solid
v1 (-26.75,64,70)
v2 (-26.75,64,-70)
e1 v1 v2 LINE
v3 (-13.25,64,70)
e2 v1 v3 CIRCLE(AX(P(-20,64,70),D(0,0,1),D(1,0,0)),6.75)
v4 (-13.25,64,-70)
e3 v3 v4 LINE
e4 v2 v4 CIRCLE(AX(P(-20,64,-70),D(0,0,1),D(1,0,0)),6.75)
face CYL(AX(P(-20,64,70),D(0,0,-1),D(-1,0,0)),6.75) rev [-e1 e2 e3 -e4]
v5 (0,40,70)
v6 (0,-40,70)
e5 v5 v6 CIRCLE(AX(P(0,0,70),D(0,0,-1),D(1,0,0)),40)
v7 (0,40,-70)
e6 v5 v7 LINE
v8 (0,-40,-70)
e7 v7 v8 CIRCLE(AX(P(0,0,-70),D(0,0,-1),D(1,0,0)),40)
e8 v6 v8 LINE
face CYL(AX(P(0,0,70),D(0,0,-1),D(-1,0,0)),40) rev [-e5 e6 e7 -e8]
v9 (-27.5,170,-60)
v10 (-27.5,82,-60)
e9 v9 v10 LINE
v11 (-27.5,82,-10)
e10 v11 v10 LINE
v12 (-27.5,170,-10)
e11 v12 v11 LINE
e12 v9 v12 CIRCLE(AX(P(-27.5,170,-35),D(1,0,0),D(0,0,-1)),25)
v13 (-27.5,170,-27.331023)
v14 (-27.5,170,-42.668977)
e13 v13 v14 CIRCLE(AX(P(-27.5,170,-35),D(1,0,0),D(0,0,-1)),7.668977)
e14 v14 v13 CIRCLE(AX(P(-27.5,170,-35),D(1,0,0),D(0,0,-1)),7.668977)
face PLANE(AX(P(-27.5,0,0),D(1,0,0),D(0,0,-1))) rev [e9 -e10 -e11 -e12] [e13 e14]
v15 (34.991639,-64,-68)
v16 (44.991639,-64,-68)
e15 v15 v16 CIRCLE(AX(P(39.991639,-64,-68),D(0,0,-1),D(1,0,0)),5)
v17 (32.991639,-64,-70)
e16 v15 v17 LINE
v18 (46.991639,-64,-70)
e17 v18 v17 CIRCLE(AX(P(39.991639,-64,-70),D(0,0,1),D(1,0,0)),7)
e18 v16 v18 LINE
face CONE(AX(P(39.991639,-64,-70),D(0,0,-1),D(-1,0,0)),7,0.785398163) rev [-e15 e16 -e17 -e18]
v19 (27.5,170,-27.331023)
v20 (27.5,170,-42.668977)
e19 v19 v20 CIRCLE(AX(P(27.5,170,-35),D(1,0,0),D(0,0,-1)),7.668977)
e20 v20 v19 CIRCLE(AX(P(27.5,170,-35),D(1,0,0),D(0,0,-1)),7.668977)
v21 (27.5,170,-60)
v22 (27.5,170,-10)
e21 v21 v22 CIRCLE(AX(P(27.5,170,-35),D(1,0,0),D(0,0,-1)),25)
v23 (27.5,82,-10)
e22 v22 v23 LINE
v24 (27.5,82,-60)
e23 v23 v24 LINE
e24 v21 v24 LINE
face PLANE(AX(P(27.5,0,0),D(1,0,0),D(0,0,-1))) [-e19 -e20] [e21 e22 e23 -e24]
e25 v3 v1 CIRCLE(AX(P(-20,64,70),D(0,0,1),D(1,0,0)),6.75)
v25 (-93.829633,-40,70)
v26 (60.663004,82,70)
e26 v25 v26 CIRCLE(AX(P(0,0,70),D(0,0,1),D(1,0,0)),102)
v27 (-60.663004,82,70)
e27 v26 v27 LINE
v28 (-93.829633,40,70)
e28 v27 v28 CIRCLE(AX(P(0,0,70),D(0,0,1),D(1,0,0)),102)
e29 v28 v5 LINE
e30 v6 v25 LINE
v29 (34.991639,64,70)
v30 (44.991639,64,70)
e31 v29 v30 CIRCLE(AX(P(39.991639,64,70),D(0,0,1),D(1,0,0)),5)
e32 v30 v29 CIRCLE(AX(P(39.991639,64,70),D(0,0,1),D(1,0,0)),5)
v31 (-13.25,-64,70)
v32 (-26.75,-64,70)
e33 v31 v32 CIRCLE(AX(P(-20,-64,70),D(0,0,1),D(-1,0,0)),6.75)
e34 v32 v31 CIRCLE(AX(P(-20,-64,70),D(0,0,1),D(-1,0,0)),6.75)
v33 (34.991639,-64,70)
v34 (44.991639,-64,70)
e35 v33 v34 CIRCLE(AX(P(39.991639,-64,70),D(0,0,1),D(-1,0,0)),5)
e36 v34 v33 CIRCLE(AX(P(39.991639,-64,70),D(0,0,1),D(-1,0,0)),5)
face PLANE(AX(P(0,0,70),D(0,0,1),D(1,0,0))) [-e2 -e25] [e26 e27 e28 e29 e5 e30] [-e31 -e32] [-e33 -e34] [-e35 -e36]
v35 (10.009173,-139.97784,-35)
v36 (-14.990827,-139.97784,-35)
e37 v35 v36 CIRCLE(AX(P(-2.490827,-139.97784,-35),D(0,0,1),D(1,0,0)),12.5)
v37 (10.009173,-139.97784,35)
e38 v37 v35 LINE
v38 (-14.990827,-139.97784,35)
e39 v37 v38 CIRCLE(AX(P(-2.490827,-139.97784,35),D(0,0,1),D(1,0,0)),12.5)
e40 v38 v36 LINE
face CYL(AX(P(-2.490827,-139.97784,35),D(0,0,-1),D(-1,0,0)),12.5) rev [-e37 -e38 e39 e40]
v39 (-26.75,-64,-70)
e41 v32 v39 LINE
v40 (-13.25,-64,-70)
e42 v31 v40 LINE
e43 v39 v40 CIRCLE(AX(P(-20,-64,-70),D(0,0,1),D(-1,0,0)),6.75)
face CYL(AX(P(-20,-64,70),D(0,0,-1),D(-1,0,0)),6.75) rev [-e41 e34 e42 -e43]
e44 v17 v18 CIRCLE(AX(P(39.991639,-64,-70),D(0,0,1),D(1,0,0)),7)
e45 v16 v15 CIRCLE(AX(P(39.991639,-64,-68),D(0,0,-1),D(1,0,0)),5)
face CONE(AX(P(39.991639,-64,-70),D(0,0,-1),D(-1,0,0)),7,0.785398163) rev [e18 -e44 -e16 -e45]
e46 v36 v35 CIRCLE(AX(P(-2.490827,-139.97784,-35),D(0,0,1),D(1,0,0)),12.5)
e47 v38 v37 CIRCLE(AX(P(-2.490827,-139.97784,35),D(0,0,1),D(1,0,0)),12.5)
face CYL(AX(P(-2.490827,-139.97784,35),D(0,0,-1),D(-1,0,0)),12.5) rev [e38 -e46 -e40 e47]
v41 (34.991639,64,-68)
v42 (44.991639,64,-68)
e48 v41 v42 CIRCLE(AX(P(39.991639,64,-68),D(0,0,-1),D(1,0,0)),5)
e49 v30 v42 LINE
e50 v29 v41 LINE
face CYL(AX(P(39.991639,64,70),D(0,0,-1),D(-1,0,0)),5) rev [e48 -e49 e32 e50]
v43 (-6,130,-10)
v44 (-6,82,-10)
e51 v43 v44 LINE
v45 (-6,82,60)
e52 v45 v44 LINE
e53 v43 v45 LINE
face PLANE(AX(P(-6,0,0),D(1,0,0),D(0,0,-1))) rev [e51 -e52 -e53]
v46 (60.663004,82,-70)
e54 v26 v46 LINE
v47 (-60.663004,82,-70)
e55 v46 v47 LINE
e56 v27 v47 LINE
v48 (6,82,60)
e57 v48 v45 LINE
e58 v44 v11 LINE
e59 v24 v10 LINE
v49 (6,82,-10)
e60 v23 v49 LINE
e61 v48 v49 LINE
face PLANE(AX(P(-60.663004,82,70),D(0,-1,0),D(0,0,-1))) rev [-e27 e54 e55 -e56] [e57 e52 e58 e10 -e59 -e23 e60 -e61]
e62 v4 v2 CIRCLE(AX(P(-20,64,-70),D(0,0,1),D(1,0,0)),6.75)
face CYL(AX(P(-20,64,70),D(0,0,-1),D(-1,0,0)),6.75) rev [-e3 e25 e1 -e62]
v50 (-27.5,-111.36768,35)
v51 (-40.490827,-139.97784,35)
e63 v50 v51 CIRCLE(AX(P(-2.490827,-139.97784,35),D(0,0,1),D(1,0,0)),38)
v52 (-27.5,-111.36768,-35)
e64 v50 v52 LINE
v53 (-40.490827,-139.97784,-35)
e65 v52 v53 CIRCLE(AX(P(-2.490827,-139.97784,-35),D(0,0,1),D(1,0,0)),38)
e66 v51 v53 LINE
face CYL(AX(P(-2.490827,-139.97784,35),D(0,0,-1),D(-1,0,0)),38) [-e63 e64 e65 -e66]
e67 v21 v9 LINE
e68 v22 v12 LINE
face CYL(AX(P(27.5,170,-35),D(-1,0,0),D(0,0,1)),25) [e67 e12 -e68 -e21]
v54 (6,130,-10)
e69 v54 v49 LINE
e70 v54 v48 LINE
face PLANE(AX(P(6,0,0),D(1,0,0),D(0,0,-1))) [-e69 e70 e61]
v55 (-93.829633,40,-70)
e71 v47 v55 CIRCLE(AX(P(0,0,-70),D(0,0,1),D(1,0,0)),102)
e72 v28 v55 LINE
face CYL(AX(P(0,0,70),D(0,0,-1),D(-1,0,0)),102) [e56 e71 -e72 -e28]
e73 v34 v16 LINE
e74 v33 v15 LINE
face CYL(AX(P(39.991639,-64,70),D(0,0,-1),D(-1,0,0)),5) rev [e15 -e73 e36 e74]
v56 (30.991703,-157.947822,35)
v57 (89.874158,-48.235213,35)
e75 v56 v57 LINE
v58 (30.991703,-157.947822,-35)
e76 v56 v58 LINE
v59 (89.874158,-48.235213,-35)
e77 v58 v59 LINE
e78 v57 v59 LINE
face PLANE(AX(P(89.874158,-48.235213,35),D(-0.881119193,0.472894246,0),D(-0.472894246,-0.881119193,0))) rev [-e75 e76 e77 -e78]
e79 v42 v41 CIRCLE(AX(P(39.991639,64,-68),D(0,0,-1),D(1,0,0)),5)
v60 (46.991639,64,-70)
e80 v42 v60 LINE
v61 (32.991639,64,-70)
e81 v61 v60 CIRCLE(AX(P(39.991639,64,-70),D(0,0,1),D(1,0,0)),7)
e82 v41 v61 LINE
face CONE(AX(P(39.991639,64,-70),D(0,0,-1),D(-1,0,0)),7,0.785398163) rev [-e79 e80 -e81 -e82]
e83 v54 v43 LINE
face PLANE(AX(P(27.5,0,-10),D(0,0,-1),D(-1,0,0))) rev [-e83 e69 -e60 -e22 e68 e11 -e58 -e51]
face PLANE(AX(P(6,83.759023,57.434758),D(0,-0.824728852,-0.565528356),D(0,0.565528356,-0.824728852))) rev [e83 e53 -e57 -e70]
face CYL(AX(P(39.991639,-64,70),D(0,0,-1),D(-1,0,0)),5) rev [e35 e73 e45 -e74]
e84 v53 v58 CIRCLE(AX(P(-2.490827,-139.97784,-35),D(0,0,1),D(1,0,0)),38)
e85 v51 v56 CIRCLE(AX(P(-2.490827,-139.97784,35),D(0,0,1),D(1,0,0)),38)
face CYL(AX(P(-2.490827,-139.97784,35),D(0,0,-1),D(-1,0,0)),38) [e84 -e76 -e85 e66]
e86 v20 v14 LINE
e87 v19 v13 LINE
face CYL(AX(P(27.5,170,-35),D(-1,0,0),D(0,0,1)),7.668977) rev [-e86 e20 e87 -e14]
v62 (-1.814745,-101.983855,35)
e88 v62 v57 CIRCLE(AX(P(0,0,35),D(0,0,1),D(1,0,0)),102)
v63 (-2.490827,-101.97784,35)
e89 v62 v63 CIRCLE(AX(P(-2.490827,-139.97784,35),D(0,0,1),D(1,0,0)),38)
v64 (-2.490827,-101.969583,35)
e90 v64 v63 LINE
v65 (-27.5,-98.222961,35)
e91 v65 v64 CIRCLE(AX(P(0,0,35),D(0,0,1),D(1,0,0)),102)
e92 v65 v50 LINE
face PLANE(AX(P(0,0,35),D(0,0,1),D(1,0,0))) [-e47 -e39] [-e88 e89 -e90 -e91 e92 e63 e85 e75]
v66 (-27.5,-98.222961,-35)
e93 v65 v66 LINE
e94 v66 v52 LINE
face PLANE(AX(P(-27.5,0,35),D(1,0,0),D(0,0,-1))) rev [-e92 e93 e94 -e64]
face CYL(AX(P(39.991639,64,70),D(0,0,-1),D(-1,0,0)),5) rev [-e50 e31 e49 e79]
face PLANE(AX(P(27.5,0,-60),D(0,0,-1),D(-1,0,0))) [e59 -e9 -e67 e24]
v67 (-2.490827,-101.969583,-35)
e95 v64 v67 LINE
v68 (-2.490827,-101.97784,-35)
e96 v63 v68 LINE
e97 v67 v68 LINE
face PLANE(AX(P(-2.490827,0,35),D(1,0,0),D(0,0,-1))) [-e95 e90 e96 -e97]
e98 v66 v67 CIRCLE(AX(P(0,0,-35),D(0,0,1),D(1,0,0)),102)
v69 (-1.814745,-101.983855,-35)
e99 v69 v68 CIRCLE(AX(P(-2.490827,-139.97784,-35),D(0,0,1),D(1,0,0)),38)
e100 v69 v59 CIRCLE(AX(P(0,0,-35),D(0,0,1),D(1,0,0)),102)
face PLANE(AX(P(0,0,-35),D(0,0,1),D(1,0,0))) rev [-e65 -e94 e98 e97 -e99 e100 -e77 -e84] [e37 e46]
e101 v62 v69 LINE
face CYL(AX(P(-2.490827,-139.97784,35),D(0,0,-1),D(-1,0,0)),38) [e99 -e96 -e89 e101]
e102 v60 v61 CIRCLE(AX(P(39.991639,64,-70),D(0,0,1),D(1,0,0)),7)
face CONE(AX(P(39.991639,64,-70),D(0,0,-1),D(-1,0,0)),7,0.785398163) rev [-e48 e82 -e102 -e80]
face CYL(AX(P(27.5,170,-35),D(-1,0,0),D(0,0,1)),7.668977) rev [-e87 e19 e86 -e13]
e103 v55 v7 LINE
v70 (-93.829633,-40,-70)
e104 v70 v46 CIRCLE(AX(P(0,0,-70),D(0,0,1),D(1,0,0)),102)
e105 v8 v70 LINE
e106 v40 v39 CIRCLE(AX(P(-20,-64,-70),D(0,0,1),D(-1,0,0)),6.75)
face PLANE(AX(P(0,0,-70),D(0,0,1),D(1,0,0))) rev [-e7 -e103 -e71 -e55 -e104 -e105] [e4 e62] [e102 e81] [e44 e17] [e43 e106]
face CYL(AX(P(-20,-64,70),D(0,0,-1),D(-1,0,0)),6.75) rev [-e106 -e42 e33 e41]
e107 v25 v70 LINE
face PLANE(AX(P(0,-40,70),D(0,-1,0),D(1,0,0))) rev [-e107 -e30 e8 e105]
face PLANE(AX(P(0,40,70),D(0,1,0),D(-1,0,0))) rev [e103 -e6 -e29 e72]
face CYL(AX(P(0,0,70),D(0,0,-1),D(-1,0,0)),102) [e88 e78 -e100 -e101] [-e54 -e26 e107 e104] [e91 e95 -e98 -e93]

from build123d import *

# Parameters (mm, degrees)
CLAMP_BODY_PROFILE_R      = 5
CLAMP_BODY_PROFILE_R_2    = 6.75
CLAMP_BODY_DEPTH          = 70
TOP_LUG_AND_RIB_PROFILE_R = 7.668976578
TOP_LUG_DEPTH             = 27.5
GUSSET_RIB_DEPTH          = 6
BOTTOM_LUG_DEPTH          = 35
EDGE_CHAMFER_2X45_SIZE    = 2


with BuildPart() as part:
    # Clamp Body Profile → Clamp Body (new, symmetric)
    with BuildSketch(Plane.XY):
        with BuildLine():
            Line((0, -40), (-93.829632846, -40))
            ThreePointArc((-93.829632846, -40), (63.213972543, -80.04994488), (60.663003552, 82))
            Line((60.663003552, 82), (-60.663003552, 82))
            ThreePointArc((-60.663003552, 82), (-80.04994488, 63.213972543), (-93.829632846, 40))
            Line((-93.829632846, 40), (0, 40))
            ThreePointArc((0, 40), (40, 0), (0, -40))
        make_face()
        with Locations((39.991638522, 64)):
            Circle(CLAMP_BODY_PROFILE_R, mode=Mode.SUBTRACT)
        with Locations((-20, 64)):
            Circle(CLAMP_BODY_PROFILE_R_2, mode=Mode.SUBTRACT)
        with Locations(Location((39.991638522, -64, 0), (0, 0, 180))):
            Circle(CLAMP_BODY_PROFILE_R, mode=Mode.SUBTRACT)
        with Locations(Location((-20, -64, 0), (0, 0, 180))):
            Circle(CLAMP_BODY_PROFILE_R_2, mode=Mode.SUBTRACT)
    extrude(amount=CLAMP_BODY_DEPTH, both=True)

    # Top Lug and Rib Profile → Top Lug (add, symmetric)
    with BuildSketch(Plane(origin=(0, 0, 0), x_dir=(0, 0, -1), z_dir=(1, 0, 0))):
        with BuildLine():
            Line((60, 82), (60, 170))
            ThreePointArc((60, 170), (35, 195), (10, 170))
            Line((10, 170), (10, 130))
            Line((10, 130), (10, 82))
            Line((10, 82), (60, 82))
        make_face()
        with Locations((35, 170)):
            Circle(TOP_LUG_AND_RIB_PROFILE_R, mode=Mode.SUBTRACT)
    extrude(amount=TOP_LUG_DEPTH, both=True)

    # Sketch6_3 → Gusset Rib (add, symmetric)
    with BuildSketch(Plane(origin=(0, 0, 0), x_dir=(0, 0, -1), z_dir=(1, 0, 0))):
        Polygon((-60, 82), (10, 82), (10, 130), align=None)
    extrude(amount=GUSSET_RIB_DEPTH, both=True)

    # Bottom Lug Profile → Bottom Lug (add, symmetric)
    with BuildSketch(Plane.XY):
        with BuildLine():
            ThreePointArc((-27.5, -111.367680386), (-26.163106523, -169.703640044), (30.991702616, -157.947821666))
            Line((30.991702616, -157.947821666), (89.874157687, -48.235213071))
            ThreePointArc((89.874157687, -48.235213071), (51.583370989, -87.995203491), (-1.814745181, -101.983855094))
            ThreePointArc((-1.814745181, -101.983855094), (-2.152772572, -101.979344048), (-2.490826719, -101.977840326))
            Line((-2.490826719, -101.977840326), (-2.490826719, -101.969582633))
            ThreePointArc((-2.490826719, -101.969582633), (-15.1119726, -100.87431925), (-27.5, -98.222960656))
            Line((-27.5, -98.222960656), (-27.5, -111.367680386))
        make_face()
        with BuildLine():
            ThreePointArc((10.009173281, -139.977840326), (-11.329661484, -148.816675091), (-2.490826719, -127.477840326))
            ThreePointArc((-2.490826719, -127.477840326), (6.348008046, -131.139005561), (10.009173281, -139.977840326))
        make_face(mode=Mode.SUBTRACT)
    extrude(amount=BOTTOM_LUG_DEPTH, both=True)

    # Edge Chamfer 2x45
    edge_chamfer_2x45_edges = [part.edges().sort_by_distance(p)[0] for p in [
        (34.991638522, 64, -70),
        (44.991638522, -64, -70),
    ]]
    chamfer(edge_chamfer_2x45_edges, length=EDGE_CHAMFER_2X45_SIZE)


solid = part.part
